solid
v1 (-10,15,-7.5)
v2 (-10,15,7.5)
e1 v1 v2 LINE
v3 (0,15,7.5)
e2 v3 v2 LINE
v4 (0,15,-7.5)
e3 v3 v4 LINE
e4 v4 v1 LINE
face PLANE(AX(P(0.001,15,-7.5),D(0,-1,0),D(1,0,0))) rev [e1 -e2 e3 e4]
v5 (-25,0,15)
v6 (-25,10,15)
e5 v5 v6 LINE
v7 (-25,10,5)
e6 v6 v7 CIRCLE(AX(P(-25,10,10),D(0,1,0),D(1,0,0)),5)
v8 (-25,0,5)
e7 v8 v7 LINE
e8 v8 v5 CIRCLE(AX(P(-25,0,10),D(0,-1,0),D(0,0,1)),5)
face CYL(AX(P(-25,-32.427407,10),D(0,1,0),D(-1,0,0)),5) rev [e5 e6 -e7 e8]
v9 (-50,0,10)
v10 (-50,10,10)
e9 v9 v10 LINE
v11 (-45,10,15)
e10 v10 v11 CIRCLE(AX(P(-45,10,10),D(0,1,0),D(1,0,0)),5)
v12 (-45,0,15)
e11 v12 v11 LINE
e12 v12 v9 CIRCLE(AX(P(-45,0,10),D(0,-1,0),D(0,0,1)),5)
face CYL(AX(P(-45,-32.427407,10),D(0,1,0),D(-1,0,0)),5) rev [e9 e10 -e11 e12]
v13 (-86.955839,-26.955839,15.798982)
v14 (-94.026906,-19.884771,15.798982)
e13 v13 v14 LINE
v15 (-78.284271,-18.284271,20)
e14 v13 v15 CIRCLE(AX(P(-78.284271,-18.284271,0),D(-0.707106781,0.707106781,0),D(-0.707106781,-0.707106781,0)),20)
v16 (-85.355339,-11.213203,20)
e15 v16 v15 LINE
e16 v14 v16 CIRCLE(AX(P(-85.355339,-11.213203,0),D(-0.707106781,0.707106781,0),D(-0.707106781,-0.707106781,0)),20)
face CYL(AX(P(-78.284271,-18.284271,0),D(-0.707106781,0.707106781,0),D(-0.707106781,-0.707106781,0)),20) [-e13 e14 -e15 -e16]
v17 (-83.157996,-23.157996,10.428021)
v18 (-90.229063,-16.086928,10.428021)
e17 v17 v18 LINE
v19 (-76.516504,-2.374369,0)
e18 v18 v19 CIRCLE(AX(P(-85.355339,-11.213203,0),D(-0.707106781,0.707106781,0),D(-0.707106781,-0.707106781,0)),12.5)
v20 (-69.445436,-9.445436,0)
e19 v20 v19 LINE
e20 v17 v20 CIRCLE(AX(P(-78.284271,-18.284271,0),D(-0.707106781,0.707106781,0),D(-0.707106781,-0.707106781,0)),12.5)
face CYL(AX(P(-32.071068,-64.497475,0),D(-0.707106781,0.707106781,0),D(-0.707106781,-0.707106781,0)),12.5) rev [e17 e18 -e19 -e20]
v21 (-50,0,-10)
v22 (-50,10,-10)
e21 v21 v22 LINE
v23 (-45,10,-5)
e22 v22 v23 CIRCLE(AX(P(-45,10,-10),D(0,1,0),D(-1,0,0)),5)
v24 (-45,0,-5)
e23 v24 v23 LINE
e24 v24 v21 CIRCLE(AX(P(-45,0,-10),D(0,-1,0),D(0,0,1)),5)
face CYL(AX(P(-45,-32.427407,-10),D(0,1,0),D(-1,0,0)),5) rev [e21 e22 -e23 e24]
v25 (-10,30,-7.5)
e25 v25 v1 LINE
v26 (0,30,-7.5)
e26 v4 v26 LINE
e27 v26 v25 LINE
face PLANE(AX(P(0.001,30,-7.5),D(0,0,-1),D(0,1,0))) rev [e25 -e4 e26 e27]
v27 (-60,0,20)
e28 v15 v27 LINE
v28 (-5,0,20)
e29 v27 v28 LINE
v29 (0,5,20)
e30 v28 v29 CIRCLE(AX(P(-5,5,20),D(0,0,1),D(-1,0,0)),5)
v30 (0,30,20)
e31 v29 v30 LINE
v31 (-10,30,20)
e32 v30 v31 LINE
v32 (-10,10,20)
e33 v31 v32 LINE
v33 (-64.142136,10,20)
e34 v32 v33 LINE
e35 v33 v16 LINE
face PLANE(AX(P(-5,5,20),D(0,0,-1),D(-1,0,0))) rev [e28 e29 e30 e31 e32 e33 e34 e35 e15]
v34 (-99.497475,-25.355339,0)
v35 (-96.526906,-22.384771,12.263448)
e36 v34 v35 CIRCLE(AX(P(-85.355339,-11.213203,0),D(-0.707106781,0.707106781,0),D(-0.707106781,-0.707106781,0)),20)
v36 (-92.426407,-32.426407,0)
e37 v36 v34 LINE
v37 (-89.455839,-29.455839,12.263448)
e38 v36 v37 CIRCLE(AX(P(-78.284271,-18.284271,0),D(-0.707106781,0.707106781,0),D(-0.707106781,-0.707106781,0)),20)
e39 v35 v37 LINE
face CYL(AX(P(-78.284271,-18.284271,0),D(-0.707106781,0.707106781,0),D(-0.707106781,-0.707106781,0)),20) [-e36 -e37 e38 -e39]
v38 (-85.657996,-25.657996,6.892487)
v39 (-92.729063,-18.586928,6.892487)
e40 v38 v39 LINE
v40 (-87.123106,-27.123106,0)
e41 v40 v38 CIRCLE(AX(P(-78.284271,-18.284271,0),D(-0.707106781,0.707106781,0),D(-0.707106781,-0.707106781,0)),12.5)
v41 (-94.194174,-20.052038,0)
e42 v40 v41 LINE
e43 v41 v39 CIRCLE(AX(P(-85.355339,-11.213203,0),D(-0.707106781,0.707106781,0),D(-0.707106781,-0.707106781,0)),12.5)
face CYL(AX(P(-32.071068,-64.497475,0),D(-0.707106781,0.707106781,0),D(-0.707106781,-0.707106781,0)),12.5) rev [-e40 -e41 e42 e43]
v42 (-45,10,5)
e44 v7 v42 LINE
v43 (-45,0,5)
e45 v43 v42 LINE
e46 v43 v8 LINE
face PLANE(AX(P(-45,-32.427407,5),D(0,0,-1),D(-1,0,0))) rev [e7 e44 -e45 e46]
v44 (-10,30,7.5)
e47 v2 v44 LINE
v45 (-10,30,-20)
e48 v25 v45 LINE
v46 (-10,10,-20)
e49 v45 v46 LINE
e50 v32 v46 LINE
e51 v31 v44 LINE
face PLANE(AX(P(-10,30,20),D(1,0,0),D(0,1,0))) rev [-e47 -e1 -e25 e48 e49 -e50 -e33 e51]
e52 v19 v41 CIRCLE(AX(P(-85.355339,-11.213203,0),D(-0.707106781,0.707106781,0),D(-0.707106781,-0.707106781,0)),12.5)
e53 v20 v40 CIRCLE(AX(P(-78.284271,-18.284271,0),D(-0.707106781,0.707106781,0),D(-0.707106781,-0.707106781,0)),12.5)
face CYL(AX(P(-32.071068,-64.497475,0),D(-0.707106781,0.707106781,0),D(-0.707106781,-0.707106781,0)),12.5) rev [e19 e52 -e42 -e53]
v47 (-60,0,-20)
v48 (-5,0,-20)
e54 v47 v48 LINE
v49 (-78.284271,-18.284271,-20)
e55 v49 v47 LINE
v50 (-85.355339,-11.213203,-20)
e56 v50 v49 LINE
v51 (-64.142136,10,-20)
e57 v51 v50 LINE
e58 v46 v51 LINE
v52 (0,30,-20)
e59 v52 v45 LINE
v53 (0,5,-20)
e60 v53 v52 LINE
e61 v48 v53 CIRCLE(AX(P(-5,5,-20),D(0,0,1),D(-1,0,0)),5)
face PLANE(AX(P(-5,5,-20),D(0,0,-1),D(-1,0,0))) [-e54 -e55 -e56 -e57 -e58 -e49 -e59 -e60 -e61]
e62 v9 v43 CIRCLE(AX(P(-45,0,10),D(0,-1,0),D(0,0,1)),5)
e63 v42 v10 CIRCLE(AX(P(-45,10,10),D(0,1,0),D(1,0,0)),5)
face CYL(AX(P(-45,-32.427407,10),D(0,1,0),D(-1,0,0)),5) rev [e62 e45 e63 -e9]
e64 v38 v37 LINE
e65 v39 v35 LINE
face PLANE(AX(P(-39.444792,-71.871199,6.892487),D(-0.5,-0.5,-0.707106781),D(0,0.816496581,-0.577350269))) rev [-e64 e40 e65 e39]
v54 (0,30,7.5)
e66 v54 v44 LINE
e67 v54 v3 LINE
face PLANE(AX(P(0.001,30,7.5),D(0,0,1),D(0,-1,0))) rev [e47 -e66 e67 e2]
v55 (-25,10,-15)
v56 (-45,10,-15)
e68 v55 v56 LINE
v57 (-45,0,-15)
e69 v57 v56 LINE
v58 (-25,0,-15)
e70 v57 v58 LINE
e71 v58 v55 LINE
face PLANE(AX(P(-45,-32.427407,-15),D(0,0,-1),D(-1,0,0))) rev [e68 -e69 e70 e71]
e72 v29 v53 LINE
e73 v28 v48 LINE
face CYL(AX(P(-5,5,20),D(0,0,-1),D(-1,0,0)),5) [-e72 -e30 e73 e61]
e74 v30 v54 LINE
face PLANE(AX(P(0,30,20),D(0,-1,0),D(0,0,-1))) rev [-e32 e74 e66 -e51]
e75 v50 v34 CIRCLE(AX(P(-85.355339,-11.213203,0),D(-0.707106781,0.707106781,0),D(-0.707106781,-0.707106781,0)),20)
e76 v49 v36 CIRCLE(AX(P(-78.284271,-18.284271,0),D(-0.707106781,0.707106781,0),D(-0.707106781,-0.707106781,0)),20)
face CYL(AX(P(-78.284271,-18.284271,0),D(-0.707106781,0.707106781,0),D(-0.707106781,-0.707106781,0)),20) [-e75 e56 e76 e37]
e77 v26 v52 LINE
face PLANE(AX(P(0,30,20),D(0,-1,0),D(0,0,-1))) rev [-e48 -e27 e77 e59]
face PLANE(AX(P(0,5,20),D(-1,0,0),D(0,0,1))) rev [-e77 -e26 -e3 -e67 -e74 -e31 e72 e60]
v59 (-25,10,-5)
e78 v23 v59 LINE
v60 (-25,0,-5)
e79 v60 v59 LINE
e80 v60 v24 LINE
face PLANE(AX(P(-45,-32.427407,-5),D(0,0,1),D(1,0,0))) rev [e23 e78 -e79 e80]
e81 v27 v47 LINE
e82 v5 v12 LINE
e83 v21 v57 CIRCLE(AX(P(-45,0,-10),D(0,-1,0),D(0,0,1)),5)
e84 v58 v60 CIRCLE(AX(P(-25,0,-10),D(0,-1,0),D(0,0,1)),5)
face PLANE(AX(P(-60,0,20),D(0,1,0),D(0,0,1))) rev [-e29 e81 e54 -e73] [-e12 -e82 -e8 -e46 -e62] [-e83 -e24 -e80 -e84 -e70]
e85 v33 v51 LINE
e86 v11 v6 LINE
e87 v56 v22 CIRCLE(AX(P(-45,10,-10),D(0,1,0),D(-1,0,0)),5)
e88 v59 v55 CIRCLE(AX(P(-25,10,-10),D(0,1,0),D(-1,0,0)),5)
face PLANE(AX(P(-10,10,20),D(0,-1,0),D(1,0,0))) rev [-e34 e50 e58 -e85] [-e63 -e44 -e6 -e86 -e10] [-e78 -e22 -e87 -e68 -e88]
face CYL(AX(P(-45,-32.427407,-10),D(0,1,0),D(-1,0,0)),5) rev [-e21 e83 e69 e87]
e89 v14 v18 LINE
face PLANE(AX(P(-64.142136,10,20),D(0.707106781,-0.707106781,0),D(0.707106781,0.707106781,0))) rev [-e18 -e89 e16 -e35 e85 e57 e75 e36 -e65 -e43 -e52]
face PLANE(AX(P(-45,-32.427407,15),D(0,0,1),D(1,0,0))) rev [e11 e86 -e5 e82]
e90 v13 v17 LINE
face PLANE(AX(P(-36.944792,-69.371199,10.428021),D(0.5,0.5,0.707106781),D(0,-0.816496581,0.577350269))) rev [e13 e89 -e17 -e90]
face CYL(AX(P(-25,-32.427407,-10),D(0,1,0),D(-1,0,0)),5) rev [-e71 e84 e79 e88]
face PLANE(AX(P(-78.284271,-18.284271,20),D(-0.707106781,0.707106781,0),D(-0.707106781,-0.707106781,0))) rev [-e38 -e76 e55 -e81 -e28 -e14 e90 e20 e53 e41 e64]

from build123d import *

# Parameters (mm, degrees)
ANGLED_BRACKET_BODY_DEPTH   = 20
GUIDE_UPRIGHT_BOSS_DEPTH    = 10
GUIDE_NOTCH_15X15_REACH     = 99.269
GUIDE_NOTCH_SKETCH_W        = 15
GUIDE_NOTCH_SKETCH_H        = 15
GUIDE_SLOTS_REACH           = 111.999
ANGLED_TRIM_CUT_45DEG_DEPTH = 96.535099634


with BuildPart() as part:
    # Bracket Profile Sketch → Angled Bracket Body (new, symmetric)
    with BuildSketch(Plane.XY):
        with BuildLine():
            Line((0, 5), (0, 30))
            Line((0, 30), (-10, 30))
            Line((-10, 30), (-10, 10))
            Line((-10, 10), (-64.142135624, 10))
            Line((-64.142135624, 10), (-85.355339059, -11.213203436))
            Line((-85.355339059, -11.213203436), (-78.284271247, -18.284271247))
            Line((-78.284271247, -18.284271247), (-60, 0))
            Line((-60, 0), (-5, 0))
            ThreePointArc((-5, 0), (-1.464466094, 1.464466094), (0, 5))
        make_face()
    extrude(amount=ANGLED_BRACKET_BODY_DEPTH, both=True)

    # Guide Upright Sketch → Guide Upright Boss (add)
    with BuildSketch(Plane(origin=(-37.071067812, 37.071067812, 0), x_dir=(0, 0, 1), z_dir=(-0.7071067811865486, 0.7071067811865465, 0))):
        with BuildLine():
            Line((-20, -68.284271247), (20, -68.284271247))
            ThreePointArc((20, -68.284271247), (0, -88.284271247), (-20, -68.284271247))
        make_face()
    extrude(amount=-GUIDE_UPRIGHT_BOSS_DEPTH)

    # Guide Notch Sketch → Guide Notch 15x15 (cut, up to next)
    with BuildSketch(Plane.ZY.offset(10), mode=Mode.PRIVATE) as guide_notch_15x15_sk1:
        with Locations((0, 22.5)):
            Rectangle(GUIDE_NOTCH_SKETCH_W, GUIDE_NOTCH_SKETCH_H)
    guide_notch_15x15_tool1 = extrude(guide_notch_15x15_sk1.sketch, amount=-GUIDE_NOTCH_15X15_REACH, mode=Mode.PRIVATE) & part.part
    add(guide_notch_15x15_tool1.solids().sort_by_distance((-10, 22.5, 0))[0], mode=Mode.SUBTRACT)

    # Guide Slots Sketch → Guide Slots (cut, up to next)
    with BuildSketch(Plane(origin=(0, 10, 0), x_dir=(1, 0, 0), z_dir=(0, 1, 0)), mode=Mode.PRIVATE) as guide_slots_sk1:
        with BuildLine():
            Line((-45, 15), (-25, 15))
            ThreePointArc((-25, 15), (-20, 10), (-25, 5))
            Line((-25, 5), (-45, 5))
            ThreePointArc((-45, 5), (-50, 10), (-45, 15))
        make_face()
    guide_slots_tool1 = extrude(guide_slots_sk1.sketch, amount=-GUIDE_SLOTS_REACH, mode=Mode.PRIVATE) & part.part
    # Guide Slots Sketch → Guide Slots (cut, up to next)
    with BuildSketch(Plane(origin=(0, 10, 0), x_dir=(1, 0, 0), z_dir=(0, 1, 0)), mode=Mode.PRIVATE) as guide_slots_sk2:
        with BuildLine():
            Line((-45, -15), (-25, -15))
            ThreePointArc((-25, -15), (-20, -10), (-25, -5))
            Line((-25, -5), (-45, -5))
            ThreePointArc((-45, -5), (-50, -10), (-45, -15))
        make_face()
    guide_slots_tool2 = extrude(guide_slots_sk2.sketch, amount=-GUIDE_SLOTS_REACH, mode=Mode.PRIVATE) & part.part
    add(guide_slots_tool1.solids().sort_by_distance((-35, 10, -10))[0], mode=Mode.SUBTRACT)
    add(guide_slots_tool2.solids().sort_by_distance((-35, 10, 10))[0], mode=Mode.SUBTRACT)

    # Angled Trim Sketch → Angled Trim Cut 45deg (cut, through all)
    with BuildSketch(Plane(origin=(-37.071067812, 37.071067812, 0), x_dir=(0, 0, 1), z_dir=(-0.7071067811865486, 0.7071067811865465, 0))):
        with BuildLine():
            Line((6.892487085, -78.712292238), (12.91897827, -84.738783423))
            Line((12.91897827, -84.738783423), (16.464043435, -81.212780777))
            Line((16.464043435, -81.212780777), (10.428020991, -75.176758332))
            ThreePointArc((10.428020991, -75.176758332), (-8.838834765, -59.445436483), (6.892487085, -78.712292238))
        make_face()
    extrude(amount=-ANGLED_TRIM_CUT_45DEG_DEPTH, mode=Mode.SUBTRACT)


solid = part.part
